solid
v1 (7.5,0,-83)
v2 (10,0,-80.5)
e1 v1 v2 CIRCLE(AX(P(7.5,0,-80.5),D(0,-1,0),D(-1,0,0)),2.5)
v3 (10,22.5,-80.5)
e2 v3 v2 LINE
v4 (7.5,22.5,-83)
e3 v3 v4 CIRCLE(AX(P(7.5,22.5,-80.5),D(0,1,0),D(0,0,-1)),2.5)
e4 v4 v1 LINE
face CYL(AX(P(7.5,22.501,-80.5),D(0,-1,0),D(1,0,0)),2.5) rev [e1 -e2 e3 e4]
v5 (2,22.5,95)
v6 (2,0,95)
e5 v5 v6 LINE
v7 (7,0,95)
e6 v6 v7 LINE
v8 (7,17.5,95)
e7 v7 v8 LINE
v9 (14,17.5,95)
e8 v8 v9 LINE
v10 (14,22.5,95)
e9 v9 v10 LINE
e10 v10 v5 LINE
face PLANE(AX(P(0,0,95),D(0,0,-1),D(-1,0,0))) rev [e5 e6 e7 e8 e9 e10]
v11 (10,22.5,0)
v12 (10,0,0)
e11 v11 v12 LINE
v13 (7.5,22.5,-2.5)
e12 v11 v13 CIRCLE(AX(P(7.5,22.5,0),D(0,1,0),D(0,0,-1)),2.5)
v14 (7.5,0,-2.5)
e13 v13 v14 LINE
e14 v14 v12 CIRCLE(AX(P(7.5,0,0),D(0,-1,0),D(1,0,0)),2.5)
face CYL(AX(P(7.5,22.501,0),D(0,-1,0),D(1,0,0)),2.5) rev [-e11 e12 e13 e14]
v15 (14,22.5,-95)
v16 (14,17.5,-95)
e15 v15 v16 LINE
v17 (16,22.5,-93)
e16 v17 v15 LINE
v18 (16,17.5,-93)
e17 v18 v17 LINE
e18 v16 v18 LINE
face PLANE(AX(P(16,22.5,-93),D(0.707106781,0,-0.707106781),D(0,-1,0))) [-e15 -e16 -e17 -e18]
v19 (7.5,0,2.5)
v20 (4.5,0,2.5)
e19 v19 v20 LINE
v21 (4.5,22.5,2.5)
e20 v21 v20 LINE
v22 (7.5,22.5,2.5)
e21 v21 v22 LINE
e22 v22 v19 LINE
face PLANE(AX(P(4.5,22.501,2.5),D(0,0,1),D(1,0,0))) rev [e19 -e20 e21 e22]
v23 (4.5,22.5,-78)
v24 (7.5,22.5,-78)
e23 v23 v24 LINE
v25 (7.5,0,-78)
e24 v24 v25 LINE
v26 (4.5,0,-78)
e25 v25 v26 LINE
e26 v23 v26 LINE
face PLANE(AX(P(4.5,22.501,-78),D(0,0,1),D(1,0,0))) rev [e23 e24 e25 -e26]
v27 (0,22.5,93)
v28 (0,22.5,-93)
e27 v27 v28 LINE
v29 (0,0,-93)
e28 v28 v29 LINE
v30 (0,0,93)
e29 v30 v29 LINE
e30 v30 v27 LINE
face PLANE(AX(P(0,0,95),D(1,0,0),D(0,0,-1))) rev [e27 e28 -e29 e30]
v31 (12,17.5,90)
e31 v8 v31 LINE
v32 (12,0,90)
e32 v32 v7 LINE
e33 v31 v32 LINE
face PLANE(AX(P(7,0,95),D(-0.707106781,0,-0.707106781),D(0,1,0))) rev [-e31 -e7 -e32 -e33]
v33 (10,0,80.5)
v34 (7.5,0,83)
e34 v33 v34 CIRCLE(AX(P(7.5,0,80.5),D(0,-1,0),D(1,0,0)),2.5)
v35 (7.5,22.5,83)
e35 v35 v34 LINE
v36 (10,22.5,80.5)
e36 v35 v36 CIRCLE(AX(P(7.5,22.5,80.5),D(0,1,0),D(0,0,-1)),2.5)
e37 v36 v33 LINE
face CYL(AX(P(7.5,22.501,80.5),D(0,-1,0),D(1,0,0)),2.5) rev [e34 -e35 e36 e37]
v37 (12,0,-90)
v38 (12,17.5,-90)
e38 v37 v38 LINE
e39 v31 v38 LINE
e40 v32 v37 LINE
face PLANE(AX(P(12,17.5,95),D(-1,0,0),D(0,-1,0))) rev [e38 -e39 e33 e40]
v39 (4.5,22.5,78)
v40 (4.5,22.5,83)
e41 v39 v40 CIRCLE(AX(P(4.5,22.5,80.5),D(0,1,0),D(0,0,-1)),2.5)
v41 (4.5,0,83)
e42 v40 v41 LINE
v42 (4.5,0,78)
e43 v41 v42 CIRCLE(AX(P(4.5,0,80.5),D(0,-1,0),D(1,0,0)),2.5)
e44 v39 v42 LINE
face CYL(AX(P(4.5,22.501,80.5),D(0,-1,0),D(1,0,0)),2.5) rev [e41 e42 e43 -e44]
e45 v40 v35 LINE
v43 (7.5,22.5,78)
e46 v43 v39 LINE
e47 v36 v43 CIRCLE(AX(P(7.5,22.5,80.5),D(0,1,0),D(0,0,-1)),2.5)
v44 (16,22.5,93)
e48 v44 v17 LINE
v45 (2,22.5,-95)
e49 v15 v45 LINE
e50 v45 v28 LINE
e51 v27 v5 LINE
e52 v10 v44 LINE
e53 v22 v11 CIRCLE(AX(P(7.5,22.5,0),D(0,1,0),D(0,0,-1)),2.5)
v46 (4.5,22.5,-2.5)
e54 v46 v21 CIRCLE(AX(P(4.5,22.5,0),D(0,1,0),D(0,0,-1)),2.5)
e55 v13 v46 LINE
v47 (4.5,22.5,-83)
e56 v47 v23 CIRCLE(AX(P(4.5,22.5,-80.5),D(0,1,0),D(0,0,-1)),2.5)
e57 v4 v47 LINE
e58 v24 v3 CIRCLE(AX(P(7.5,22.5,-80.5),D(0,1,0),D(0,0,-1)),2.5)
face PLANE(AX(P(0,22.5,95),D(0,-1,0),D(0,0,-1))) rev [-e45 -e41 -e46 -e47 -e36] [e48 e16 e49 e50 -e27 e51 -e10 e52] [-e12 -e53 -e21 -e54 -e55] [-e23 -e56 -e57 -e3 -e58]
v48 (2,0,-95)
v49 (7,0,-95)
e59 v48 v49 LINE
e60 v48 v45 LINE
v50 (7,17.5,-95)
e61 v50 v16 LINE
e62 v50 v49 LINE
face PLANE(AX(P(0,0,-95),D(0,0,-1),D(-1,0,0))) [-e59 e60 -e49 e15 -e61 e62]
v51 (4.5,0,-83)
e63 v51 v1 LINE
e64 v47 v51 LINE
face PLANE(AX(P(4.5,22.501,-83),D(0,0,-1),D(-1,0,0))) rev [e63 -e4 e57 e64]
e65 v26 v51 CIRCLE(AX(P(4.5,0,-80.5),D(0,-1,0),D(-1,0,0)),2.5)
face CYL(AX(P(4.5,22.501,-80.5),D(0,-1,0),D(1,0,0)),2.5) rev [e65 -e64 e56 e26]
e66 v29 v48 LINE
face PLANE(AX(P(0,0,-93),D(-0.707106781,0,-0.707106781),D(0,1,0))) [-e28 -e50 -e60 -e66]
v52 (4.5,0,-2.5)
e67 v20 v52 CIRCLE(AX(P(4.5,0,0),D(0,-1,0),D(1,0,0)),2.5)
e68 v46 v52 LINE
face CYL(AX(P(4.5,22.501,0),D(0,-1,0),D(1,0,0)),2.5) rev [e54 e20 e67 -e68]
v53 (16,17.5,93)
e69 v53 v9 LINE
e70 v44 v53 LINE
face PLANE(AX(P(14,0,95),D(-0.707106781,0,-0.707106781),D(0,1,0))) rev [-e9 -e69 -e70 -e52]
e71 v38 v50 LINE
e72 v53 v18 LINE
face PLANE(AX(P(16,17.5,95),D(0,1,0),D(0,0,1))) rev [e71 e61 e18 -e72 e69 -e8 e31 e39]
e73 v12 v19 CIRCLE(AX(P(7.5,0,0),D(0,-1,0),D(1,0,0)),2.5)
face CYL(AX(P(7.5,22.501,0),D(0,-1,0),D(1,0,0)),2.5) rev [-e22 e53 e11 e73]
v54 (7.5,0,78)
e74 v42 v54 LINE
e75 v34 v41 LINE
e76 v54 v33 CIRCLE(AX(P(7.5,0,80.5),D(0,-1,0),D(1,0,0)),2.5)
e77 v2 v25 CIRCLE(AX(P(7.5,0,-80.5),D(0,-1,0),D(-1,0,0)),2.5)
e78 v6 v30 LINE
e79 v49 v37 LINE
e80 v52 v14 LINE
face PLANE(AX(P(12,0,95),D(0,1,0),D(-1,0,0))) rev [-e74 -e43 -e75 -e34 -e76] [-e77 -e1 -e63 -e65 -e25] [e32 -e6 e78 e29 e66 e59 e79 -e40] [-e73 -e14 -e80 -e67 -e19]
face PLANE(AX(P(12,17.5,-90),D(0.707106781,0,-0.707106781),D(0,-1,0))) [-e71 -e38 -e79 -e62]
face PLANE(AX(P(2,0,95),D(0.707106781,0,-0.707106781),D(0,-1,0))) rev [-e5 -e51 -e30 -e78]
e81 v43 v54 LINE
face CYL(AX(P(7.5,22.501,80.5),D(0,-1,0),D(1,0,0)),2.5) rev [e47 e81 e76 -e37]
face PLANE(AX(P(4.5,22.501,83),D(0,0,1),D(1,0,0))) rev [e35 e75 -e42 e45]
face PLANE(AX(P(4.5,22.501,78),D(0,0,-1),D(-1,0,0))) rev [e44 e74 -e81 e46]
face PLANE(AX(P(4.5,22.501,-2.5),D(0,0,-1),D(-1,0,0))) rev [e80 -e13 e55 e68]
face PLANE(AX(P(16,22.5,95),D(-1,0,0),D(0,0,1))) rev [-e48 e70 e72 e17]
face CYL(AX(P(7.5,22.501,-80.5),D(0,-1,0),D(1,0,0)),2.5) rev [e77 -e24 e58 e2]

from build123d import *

# Parameters (mm, degrees)
EXTRUDE_1_DEPTH     = 95
CHAMFER_1_SIZE      = 5
CHAMFER_2_SIZE      = 2
CUT_EXTRUDE_1_REACH = 100.931


with BuildPart() as part:
    # 草图1 → 凸台-拉伸1 (new, symmetric)
    with BuildSketch(Plane.XY):
        Polygon((0, 0), (0, 22.5), (16, 22.5), (16, 17.5), (12, 17.5), (12, 0), align=None)
    extrude(amount=EXTRUDE_1_DEPTH, both=True)

    # 倒角1
    chamfer_1_edges = [part.edges().sort_by_distance(p)[0] for p in [
        (12, 8.75, 95),
        (12, 8.75, -95),
    ]]
    chamfer(chamfer_1_edges, length=CHAMFER_1_SIZE)

    # 倒角2
    chamfer_2_edges = [part.edges().sort_by_distance(p)[0] for p in [
        (16, 20, 95),
        (0, 11.25, 95),
        (0, 11.25, -95),
        (16, 20, -95),
    ]]
    chamfer(chamfer_2_edges, length=CHAMFER_2_SIZE)

    # 草图2 → 切除-拉伸1 (cut, up to next)
    with BuildSketch(Plane.XZ, mode=Mode.PRIVATE) as cut_extrude_1_sk1:
        with BuildLine():
            Line((4.5, 83), (7.5, 83))
            ThreePointArc((7.5, 83), (10, 80.5), (7.5, 78))
            Line((7.5, 78), (4.5, 78))
            ThreePointArc((4.5, 78), (2, 80.5), (4.5, 83))
        make_face()
    cut_extrude_1_tool1 = extrude(cut_extrude_1_sk1.sketch, amount=-CUT_EXTRUDE_1_REACH, mode=Mode.PRIVATE) & part.part
    # 草图2 → 切除-拉伸1 (cut, up to next)
    with BuildSketch(Plane.XZ, mode=Mode.PRIVATE) as cut_extrude_1_sk2:
        with BuildLine():
            Line((4.5, 2.5), (7.5, 2.5))
            ThreePointArc((7.5, 2.5), (10, 0), (7.5, -2.5))
            Line((7.5, -2.5), (4.5, -2.5))
            ThreePointArc((4.5, -2.5), (2, 0), (4.5, 2.5))
        make_face()
    cut_extrude_1_tool2 = extrude(cut_extrude_1_sk2.sketch, amount=-CUT_EXTRUDE_1_REACH, mode=Mode.PRIVATE) & part.part
    # 草图2 → 切除-拉伸1 (cut, up to next)
    with BuildSketch(Plane.XZ, mode=Mode.PRIVATE) as cut_extrude_1_sk3:
        with BuildLine():
            Line((4.5, -83), (7.5, -83))
            ThreePointArc((7.5, -83), (10, -80.5), (7.5, -78))
            Line((7.5, -78), (4.5, -78))
            ThreePointArc((4.5, -78), (2, -80.5), (4.5, -83))
        make_face()
    cut_extrude_1_tool3 = extrude(cut_extrude_1_sk3.sketch, amount=-CUT_EXTRUDE_1_REACH, mode=Mode.PRIVATE) & part.part
    add(cut_extrude_1_tool1.solids().sort_by_distance((6, 0, 80.5))[0], mode=Mode.SUBTRACT)
    add(cut_extrude_1_tool2.solids().sort_by_distance((6, 0, 0))[0], mode=Mode.SUBTRACT)
    add(cut_extrude_1_tool3.solids().sort_by_distance((6, 0, -80.5))[0], mode=Mode.SUBTRACT)


solid = part.part
